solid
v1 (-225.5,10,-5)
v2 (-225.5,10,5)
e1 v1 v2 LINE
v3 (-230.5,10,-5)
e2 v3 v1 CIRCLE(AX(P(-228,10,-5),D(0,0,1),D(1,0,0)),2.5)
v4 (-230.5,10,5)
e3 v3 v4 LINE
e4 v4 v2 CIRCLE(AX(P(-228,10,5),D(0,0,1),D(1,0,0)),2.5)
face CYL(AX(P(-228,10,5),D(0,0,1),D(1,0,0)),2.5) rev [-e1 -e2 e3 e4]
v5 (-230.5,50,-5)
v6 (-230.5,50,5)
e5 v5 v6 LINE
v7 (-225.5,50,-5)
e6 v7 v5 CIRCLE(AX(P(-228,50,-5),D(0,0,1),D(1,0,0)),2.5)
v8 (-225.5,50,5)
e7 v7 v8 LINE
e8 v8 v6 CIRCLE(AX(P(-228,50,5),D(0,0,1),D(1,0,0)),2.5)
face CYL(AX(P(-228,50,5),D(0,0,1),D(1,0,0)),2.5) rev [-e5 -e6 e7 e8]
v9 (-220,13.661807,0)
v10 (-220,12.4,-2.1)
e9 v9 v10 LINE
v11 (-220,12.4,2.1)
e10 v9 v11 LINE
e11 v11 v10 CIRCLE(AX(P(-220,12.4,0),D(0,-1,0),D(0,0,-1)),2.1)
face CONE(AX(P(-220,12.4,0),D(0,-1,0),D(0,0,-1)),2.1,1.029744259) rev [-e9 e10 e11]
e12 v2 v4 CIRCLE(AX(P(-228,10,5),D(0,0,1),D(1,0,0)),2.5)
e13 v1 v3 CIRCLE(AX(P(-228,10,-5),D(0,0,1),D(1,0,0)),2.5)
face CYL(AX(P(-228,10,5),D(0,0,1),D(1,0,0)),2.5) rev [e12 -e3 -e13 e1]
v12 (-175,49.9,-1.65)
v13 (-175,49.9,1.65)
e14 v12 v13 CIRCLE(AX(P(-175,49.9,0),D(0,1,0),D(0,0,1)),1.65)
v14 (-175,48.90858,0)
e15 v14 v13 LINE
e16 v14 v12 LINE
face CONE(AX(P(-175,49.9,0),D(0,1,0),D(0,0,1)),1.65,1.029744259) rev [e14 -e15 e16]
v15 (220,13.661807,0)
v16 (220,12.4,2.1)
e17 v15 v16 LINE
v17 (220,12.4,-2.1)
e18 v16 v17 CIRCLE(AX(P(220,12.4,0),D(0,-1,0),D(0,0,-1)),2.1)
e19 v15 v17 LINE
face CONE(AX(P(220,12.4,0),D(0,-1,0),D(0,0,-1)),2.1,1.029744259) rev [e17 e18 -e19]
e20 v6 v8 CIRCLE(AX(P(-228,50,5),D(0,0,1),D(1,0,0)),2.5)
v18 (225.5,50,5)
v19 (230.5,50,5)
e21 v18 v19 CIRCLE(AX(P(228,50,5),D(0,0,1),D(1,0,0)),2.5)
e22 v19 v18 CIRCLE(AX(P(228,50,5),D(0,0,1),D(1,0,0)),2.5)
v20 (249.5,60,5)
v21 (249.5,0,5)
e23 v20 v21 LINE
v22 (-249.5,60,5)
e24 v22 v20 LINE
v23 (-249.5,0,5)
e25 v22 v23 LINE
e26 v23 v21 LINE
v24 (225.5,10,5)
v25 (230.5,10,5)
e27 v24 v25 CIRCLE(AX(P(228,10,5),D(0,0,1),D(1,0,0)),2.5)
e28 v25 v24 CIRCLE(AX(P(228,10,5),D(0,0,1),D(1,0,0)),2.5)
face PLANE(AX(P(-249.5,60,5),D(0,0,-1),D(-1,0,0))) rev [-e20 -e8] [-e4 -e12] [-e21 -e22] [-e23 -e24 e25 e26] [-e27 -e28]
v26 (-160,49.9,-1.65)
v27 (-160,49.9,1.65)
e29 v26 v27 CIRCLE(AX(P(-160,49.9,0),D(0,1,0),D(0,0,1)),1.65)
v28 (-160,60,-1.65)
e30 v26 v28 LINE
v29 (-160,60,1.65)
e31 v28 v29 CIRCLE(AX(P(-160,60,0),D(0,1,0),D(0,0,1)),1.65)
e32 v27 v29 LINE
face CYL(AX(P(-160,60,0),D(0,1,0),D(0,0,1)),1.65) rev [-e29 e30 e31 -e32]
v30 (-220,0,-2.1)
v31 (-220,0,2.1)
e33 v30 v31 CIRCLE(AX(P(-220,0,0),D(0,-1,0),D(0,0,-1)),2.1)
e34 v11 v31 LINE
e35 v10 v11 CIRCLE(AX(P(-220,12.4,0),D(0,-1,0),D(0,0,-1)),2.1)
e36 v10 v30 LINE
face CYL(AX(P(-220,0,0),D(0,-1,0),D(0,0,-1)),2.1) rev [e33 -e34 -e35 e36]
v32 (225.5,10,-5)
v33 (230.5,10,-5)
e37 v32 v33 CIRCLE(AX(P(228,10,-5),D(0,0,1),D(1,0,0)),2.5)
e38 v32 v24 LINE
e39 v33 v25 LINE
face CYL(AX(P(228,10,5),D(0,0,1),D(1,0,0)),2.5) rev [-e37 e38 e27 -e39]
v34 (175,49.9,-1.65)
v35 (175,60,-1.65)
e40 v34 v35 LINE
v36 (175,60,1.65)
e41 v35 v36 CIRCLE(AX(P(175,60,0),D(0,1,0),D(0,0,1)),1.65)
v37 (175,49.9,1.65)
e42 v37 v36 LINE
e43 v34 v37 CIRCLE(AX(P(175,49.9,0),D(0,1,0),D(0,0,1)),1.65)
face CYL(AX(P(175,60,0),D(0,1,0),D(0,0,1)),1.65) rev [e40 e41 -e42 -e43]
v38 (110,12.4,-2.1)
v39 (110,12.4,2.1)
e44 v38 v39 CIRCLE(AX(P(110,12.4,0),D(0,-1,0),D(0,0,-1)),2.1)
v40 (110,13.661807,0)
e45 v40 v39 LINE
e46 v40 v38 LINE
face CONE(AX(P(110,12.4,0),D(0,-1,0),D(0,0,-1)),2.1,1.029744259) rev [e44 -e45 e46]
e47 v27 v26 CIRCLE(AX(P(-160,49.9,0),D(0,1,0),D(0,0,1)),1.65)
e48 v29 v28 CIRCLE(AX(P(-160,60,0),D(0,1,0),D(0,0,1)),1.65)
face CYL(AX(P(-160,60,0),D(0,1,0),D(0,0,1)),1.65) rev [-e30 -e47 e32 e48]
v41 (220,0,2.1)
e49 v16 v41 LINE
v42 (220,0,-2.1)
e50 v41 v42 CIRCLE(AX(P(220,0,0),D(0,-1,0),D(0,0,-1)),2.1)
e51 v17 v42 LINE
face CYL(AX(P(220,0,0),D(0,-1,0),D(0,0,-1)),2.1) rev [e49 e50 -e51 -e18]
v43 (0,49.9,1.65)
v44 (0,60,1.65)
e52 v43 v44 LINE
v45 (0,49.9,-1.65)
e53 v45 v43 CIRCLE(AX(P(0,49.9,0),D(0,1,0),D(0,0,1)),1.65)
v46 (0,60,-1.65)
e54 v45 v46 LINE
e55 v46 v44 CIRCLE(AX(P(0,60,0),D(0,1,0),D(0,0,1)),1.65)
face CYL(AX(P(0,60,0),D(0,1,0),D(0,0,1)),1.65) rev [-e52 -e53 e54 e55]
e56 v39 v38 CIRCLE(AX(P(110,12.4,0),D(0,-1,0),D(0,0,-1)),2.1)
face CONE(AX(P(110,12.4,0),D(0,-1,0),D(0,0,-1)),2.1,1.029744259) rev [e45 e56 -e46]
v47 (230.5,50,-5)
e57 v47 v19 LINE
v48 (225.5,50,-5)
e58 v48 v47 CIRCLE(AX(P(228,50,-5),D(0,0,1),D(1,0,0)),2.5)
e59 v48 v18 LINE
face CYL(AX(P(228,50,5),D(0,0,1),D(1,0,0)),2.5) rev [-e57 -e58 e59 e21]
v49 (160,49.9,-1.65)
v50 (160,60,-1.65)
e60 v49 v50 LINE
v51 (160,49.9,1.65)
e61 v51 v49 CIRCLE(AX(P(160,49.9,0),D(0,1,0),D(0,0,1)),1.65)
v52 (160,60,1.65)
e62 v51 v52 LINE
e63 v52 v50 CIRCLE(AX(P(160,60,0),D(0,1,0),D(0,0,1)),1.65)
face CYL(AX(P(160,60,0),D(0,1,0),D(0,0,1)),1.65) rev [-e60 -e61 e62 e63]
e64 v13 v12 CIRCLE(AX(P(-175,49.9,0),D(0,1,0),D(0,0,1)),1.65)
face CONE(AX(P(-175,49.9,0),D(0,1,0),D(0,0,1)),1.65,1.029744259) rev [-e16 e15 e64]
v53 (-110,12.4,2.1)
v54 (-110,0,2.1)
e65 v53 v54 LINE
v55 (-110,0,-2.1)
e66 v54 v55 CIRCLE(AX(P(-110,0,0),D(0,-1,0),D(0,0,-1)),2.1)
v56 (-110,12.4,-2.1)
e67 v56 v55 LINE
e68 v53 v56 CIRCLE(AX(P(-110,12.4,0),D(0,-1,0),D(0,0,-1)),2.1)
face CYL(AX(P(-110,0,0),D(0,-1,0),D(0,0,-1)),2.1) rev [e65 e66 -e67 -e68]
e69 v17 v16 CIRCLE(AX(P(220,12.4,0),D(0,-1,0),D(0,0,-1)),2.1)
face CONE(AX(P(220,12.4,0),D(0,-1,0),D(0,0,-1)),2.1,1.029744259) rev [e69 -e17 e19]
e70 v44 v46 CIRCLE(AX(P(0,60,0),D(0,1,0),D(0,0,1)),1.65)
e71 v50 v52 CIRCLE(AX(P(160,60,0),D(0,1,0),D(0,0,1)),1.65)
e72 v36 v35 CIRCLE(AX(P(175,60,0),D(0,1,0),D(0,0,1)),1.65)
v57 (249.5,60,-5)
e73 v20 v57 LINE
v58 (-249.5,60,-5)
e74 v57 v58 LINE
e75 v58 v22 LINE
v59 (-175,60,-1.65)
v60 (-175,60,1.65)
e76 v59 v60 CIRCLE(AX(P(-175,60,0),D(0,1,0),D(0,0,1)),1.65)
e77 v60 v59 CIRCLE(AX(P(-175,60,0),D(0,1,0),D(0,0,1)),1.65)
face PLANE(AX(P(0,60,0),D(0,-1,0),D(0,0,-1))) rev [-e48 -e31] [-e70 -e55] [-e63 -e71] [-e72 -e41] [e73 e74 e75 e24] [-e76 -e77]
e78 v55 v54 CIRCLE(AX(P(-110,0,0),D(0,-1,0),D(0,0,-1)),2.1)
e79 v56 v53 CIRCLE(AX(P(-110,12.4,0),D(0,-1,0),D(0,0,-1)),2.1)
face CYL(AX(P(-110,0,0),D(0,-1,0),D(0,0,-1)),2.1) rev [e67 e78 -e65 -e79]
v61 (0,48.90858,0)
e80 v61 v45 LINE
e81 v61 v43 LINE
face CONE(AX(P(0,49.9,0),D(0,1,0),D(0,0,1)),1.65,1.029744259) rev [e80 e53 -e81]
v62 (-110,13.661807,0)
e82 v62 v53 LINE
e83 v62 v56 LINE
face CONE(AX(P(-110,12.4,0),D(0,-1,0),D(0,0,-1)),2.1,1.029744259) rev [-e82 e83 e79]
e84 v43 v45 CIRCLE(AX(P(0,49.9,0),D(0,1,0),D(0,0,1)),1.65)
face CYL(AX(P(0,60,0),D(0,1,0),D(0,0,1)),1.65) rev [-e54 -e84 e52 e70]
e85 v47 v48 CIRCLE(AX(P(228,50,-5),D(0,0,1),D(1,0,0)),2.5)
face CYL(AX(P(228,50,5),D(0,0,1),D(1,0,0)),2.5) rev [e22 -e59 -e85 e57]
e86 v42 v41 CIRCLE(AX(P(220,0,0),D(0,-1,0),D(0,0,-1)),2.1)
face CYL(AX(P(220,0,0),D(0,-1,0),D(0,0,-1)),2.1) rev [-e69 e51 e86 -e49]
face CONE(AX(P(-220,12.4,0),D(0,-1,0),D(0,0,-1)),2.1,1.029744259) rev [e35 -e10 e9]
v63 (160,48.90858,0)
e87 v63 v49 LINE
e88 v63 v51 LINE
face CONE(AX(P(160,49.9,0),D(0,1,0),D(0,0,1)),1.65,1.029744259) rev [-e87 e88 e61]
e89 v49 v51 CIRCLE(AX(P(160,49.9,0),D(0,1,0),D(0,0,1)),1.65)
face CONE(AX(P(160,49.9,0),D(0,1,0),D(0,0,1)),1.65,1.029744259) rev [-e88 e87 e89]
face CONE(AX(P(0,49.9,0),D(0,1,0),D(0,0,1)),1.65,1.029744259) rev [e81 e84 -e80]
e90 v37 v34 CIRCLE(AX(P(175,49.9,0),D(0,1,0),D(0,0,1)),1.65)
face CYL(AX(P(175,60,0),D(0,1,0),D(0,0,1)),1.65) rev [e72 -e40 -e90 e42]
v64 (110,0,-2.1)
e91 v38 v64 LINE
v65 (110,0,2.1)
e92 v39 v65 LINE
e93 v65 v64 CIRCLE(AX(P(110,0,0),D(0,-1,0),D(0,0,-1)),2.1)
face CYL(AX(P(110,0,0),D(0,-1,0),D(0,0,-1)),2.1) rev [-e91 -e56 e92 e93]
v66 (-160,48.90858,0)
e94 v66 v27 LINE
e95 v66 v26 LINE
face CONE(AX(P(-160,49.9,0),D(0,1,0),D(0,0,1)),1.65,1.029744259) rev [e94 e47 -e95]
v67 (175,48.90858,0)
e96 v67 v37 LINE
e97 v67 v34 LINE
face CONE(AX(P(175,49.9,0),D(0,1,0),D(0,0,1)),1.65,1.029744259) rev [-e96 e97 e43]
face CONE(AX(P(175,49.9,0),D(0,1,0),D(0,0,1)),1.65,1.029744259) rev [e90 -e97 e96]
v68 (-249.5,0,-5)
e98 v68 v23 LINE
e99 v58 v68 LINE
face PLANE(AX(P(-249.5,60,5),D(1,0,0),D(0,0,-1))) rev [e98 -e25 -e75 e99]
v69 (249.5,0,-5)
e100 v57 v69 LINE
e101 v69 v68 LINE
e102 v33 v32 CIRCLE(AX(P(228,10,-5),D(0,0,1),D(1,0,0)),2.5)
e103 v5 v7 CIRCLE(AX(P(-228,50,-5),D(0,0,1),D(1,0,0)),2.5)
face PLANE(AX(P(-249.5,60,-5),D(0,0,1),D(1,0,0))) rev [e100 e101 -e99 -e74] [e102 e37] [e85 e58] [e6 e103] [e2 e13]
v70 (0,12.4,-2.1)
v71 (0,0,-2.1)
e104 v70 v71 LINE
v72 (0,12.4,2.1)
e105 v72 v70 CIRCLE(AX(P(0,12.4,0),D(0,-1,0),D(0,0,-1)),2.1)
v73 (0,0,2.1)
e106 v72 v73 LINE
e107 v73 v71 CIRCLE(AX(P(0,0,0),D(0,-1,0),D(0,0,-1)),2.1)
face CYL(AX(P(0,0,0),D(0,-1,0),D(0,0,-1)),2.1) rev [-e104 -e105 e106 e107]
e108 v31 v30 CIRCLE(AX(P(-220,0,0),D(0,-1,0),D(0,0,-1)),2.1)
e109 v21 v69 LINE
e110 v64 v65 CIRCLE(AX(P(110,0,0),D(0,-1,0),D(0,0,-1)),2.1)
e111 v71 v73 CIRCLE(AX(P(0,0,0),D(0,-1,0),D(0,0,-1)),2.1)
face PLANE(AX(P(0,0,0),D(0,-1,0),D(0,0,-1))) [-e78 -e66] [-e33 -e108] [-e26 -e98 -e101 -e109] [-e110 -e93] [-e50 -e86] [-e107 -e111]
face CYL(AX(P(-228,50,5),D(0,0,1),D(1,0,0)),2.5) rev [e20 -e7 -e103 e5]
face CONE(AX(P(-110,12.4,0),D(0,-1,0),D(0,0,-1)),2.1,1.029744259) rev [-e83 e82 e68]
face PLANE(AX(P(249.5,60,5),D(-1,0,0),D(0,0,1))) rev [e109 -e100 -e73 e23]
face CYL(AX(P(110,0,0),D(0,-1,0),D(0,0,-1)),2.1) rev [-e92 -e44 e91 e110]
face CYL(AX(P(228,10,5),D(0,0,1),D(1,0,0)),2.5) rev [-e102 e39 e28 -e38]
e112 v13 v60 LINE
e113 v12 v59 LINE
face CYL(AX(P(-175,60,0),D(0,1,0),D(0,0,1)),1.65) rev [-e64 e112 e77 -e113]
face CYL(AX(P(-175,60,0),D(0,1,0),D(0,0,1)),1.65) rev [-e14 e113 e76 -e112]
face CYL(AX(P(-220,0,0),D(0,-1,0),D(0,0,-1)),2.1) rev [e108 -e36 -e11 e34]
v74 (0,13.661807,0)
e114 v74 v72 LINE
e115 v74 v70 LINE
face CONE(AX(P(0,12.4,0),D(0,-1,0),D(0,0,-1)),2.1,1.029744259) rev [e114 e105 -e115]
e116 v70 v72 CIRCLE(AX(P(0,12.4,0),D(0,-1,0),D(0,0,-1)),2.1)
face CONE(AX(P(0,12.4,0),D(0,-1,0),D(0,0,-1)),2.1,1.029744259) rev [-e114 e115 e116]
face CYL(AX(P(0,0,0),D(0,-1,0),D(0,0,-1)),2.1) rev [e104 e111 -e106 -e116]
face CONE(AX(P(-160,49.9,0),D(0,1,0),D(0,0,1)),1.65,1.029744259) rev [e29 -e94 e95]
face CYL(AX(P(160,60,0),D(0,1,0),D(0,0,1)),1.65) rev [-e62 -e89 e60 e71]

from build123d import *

# Parameters (mm, degrees)
SKETCH_1_W             = 499
SKETCH_1_H             = 10
EXTRUDE_1_DEPTH        = 60
HOLE_WIZARD_M5_1_D     = 4.2
HOLE_WIZARD_M5_1_DEPTH = 12.4
HOLE_WIZARD_M5_1_TIP   = 1.2618073
HOLE_WIZARD_M6_1_D     = 5
HOLE_WIZARD_M4_1_D     = 3.3
HOLE_WIZARD_M4_1_DEPTH = 10.1
HOLE_WIZARD_M4_1_TIP   = 0.991420021


with BuildPart() as part:
    # 草图1 → 凸台-拉伸1 (new body)
    with BuildSketch(Plane(origin=(0, 0, 0), x_dir=(1, 0, 0), z_dir=(0, 1, 0))):
        Rectangle(SKETCH_1_W, SKETCH_1_H)
    extrude(amount=EXTRUDE_1_DEPTH)

    # M5 螺纹孔1
    with Locations(Plane(origin=(0, 0, 0), x_dir=(-1, 0, 0), z_dir=(0, -1, 0))):
        with Locations((-220, 0), (-110, 0), (0, 0), (110, 0), (220, 0)):
            Hole(HOLE_WIZARD_M5_1_D / 2, depth=HOLE_WIZARD_M5_1_DEPTH)
            with Locations((0, 0, -(HOLE_WIZARD_M5_1_DEPTH + HOLE_WIZARD_M5_1_TIP / 2))):  # 118° drill point
                Cone(0, HOLE_WIZARD_M5_1_D / 2, HOLE_WIZARD_M5_1_TIP, mode=Mode.SUBTRACT)

    # M6 螺纹孔1 (through all)
    with Locations(Plane.XY.offset(5)):
        with Locations((228, 50), (228, 10), (-228, 10), (-228, 50)):
            Hole(HOLE_WIZARD_M6_1_D / 2)

    # M4 螺纹孔1
    with Locations(Plane(origin=(0, 60, 0), x_dir=(1, 0, 0), z_dir=(0, 1, 0))):
        with Locations((0, 0), (-175, 0), (175, 0), (-160, 0), (160, 0)):
            Hole(HOLE_WIZARD_M4_1_D / 2, depth=HOLE_WIZARD_M4_1_DEPTH)
            with Locations((0, 0, -(HOLE_WIZARD_M4_1_DEPTH + HOLE_WIZARD_M4_1_TIP / 2))):  # 118° drill point
                Cone(0, HOLE_WIZARD_M4_1_D / 2, HOLE_WIZARD_M4_1_TIP, mode=Mode.SUBTRACT)


solid = part.part
